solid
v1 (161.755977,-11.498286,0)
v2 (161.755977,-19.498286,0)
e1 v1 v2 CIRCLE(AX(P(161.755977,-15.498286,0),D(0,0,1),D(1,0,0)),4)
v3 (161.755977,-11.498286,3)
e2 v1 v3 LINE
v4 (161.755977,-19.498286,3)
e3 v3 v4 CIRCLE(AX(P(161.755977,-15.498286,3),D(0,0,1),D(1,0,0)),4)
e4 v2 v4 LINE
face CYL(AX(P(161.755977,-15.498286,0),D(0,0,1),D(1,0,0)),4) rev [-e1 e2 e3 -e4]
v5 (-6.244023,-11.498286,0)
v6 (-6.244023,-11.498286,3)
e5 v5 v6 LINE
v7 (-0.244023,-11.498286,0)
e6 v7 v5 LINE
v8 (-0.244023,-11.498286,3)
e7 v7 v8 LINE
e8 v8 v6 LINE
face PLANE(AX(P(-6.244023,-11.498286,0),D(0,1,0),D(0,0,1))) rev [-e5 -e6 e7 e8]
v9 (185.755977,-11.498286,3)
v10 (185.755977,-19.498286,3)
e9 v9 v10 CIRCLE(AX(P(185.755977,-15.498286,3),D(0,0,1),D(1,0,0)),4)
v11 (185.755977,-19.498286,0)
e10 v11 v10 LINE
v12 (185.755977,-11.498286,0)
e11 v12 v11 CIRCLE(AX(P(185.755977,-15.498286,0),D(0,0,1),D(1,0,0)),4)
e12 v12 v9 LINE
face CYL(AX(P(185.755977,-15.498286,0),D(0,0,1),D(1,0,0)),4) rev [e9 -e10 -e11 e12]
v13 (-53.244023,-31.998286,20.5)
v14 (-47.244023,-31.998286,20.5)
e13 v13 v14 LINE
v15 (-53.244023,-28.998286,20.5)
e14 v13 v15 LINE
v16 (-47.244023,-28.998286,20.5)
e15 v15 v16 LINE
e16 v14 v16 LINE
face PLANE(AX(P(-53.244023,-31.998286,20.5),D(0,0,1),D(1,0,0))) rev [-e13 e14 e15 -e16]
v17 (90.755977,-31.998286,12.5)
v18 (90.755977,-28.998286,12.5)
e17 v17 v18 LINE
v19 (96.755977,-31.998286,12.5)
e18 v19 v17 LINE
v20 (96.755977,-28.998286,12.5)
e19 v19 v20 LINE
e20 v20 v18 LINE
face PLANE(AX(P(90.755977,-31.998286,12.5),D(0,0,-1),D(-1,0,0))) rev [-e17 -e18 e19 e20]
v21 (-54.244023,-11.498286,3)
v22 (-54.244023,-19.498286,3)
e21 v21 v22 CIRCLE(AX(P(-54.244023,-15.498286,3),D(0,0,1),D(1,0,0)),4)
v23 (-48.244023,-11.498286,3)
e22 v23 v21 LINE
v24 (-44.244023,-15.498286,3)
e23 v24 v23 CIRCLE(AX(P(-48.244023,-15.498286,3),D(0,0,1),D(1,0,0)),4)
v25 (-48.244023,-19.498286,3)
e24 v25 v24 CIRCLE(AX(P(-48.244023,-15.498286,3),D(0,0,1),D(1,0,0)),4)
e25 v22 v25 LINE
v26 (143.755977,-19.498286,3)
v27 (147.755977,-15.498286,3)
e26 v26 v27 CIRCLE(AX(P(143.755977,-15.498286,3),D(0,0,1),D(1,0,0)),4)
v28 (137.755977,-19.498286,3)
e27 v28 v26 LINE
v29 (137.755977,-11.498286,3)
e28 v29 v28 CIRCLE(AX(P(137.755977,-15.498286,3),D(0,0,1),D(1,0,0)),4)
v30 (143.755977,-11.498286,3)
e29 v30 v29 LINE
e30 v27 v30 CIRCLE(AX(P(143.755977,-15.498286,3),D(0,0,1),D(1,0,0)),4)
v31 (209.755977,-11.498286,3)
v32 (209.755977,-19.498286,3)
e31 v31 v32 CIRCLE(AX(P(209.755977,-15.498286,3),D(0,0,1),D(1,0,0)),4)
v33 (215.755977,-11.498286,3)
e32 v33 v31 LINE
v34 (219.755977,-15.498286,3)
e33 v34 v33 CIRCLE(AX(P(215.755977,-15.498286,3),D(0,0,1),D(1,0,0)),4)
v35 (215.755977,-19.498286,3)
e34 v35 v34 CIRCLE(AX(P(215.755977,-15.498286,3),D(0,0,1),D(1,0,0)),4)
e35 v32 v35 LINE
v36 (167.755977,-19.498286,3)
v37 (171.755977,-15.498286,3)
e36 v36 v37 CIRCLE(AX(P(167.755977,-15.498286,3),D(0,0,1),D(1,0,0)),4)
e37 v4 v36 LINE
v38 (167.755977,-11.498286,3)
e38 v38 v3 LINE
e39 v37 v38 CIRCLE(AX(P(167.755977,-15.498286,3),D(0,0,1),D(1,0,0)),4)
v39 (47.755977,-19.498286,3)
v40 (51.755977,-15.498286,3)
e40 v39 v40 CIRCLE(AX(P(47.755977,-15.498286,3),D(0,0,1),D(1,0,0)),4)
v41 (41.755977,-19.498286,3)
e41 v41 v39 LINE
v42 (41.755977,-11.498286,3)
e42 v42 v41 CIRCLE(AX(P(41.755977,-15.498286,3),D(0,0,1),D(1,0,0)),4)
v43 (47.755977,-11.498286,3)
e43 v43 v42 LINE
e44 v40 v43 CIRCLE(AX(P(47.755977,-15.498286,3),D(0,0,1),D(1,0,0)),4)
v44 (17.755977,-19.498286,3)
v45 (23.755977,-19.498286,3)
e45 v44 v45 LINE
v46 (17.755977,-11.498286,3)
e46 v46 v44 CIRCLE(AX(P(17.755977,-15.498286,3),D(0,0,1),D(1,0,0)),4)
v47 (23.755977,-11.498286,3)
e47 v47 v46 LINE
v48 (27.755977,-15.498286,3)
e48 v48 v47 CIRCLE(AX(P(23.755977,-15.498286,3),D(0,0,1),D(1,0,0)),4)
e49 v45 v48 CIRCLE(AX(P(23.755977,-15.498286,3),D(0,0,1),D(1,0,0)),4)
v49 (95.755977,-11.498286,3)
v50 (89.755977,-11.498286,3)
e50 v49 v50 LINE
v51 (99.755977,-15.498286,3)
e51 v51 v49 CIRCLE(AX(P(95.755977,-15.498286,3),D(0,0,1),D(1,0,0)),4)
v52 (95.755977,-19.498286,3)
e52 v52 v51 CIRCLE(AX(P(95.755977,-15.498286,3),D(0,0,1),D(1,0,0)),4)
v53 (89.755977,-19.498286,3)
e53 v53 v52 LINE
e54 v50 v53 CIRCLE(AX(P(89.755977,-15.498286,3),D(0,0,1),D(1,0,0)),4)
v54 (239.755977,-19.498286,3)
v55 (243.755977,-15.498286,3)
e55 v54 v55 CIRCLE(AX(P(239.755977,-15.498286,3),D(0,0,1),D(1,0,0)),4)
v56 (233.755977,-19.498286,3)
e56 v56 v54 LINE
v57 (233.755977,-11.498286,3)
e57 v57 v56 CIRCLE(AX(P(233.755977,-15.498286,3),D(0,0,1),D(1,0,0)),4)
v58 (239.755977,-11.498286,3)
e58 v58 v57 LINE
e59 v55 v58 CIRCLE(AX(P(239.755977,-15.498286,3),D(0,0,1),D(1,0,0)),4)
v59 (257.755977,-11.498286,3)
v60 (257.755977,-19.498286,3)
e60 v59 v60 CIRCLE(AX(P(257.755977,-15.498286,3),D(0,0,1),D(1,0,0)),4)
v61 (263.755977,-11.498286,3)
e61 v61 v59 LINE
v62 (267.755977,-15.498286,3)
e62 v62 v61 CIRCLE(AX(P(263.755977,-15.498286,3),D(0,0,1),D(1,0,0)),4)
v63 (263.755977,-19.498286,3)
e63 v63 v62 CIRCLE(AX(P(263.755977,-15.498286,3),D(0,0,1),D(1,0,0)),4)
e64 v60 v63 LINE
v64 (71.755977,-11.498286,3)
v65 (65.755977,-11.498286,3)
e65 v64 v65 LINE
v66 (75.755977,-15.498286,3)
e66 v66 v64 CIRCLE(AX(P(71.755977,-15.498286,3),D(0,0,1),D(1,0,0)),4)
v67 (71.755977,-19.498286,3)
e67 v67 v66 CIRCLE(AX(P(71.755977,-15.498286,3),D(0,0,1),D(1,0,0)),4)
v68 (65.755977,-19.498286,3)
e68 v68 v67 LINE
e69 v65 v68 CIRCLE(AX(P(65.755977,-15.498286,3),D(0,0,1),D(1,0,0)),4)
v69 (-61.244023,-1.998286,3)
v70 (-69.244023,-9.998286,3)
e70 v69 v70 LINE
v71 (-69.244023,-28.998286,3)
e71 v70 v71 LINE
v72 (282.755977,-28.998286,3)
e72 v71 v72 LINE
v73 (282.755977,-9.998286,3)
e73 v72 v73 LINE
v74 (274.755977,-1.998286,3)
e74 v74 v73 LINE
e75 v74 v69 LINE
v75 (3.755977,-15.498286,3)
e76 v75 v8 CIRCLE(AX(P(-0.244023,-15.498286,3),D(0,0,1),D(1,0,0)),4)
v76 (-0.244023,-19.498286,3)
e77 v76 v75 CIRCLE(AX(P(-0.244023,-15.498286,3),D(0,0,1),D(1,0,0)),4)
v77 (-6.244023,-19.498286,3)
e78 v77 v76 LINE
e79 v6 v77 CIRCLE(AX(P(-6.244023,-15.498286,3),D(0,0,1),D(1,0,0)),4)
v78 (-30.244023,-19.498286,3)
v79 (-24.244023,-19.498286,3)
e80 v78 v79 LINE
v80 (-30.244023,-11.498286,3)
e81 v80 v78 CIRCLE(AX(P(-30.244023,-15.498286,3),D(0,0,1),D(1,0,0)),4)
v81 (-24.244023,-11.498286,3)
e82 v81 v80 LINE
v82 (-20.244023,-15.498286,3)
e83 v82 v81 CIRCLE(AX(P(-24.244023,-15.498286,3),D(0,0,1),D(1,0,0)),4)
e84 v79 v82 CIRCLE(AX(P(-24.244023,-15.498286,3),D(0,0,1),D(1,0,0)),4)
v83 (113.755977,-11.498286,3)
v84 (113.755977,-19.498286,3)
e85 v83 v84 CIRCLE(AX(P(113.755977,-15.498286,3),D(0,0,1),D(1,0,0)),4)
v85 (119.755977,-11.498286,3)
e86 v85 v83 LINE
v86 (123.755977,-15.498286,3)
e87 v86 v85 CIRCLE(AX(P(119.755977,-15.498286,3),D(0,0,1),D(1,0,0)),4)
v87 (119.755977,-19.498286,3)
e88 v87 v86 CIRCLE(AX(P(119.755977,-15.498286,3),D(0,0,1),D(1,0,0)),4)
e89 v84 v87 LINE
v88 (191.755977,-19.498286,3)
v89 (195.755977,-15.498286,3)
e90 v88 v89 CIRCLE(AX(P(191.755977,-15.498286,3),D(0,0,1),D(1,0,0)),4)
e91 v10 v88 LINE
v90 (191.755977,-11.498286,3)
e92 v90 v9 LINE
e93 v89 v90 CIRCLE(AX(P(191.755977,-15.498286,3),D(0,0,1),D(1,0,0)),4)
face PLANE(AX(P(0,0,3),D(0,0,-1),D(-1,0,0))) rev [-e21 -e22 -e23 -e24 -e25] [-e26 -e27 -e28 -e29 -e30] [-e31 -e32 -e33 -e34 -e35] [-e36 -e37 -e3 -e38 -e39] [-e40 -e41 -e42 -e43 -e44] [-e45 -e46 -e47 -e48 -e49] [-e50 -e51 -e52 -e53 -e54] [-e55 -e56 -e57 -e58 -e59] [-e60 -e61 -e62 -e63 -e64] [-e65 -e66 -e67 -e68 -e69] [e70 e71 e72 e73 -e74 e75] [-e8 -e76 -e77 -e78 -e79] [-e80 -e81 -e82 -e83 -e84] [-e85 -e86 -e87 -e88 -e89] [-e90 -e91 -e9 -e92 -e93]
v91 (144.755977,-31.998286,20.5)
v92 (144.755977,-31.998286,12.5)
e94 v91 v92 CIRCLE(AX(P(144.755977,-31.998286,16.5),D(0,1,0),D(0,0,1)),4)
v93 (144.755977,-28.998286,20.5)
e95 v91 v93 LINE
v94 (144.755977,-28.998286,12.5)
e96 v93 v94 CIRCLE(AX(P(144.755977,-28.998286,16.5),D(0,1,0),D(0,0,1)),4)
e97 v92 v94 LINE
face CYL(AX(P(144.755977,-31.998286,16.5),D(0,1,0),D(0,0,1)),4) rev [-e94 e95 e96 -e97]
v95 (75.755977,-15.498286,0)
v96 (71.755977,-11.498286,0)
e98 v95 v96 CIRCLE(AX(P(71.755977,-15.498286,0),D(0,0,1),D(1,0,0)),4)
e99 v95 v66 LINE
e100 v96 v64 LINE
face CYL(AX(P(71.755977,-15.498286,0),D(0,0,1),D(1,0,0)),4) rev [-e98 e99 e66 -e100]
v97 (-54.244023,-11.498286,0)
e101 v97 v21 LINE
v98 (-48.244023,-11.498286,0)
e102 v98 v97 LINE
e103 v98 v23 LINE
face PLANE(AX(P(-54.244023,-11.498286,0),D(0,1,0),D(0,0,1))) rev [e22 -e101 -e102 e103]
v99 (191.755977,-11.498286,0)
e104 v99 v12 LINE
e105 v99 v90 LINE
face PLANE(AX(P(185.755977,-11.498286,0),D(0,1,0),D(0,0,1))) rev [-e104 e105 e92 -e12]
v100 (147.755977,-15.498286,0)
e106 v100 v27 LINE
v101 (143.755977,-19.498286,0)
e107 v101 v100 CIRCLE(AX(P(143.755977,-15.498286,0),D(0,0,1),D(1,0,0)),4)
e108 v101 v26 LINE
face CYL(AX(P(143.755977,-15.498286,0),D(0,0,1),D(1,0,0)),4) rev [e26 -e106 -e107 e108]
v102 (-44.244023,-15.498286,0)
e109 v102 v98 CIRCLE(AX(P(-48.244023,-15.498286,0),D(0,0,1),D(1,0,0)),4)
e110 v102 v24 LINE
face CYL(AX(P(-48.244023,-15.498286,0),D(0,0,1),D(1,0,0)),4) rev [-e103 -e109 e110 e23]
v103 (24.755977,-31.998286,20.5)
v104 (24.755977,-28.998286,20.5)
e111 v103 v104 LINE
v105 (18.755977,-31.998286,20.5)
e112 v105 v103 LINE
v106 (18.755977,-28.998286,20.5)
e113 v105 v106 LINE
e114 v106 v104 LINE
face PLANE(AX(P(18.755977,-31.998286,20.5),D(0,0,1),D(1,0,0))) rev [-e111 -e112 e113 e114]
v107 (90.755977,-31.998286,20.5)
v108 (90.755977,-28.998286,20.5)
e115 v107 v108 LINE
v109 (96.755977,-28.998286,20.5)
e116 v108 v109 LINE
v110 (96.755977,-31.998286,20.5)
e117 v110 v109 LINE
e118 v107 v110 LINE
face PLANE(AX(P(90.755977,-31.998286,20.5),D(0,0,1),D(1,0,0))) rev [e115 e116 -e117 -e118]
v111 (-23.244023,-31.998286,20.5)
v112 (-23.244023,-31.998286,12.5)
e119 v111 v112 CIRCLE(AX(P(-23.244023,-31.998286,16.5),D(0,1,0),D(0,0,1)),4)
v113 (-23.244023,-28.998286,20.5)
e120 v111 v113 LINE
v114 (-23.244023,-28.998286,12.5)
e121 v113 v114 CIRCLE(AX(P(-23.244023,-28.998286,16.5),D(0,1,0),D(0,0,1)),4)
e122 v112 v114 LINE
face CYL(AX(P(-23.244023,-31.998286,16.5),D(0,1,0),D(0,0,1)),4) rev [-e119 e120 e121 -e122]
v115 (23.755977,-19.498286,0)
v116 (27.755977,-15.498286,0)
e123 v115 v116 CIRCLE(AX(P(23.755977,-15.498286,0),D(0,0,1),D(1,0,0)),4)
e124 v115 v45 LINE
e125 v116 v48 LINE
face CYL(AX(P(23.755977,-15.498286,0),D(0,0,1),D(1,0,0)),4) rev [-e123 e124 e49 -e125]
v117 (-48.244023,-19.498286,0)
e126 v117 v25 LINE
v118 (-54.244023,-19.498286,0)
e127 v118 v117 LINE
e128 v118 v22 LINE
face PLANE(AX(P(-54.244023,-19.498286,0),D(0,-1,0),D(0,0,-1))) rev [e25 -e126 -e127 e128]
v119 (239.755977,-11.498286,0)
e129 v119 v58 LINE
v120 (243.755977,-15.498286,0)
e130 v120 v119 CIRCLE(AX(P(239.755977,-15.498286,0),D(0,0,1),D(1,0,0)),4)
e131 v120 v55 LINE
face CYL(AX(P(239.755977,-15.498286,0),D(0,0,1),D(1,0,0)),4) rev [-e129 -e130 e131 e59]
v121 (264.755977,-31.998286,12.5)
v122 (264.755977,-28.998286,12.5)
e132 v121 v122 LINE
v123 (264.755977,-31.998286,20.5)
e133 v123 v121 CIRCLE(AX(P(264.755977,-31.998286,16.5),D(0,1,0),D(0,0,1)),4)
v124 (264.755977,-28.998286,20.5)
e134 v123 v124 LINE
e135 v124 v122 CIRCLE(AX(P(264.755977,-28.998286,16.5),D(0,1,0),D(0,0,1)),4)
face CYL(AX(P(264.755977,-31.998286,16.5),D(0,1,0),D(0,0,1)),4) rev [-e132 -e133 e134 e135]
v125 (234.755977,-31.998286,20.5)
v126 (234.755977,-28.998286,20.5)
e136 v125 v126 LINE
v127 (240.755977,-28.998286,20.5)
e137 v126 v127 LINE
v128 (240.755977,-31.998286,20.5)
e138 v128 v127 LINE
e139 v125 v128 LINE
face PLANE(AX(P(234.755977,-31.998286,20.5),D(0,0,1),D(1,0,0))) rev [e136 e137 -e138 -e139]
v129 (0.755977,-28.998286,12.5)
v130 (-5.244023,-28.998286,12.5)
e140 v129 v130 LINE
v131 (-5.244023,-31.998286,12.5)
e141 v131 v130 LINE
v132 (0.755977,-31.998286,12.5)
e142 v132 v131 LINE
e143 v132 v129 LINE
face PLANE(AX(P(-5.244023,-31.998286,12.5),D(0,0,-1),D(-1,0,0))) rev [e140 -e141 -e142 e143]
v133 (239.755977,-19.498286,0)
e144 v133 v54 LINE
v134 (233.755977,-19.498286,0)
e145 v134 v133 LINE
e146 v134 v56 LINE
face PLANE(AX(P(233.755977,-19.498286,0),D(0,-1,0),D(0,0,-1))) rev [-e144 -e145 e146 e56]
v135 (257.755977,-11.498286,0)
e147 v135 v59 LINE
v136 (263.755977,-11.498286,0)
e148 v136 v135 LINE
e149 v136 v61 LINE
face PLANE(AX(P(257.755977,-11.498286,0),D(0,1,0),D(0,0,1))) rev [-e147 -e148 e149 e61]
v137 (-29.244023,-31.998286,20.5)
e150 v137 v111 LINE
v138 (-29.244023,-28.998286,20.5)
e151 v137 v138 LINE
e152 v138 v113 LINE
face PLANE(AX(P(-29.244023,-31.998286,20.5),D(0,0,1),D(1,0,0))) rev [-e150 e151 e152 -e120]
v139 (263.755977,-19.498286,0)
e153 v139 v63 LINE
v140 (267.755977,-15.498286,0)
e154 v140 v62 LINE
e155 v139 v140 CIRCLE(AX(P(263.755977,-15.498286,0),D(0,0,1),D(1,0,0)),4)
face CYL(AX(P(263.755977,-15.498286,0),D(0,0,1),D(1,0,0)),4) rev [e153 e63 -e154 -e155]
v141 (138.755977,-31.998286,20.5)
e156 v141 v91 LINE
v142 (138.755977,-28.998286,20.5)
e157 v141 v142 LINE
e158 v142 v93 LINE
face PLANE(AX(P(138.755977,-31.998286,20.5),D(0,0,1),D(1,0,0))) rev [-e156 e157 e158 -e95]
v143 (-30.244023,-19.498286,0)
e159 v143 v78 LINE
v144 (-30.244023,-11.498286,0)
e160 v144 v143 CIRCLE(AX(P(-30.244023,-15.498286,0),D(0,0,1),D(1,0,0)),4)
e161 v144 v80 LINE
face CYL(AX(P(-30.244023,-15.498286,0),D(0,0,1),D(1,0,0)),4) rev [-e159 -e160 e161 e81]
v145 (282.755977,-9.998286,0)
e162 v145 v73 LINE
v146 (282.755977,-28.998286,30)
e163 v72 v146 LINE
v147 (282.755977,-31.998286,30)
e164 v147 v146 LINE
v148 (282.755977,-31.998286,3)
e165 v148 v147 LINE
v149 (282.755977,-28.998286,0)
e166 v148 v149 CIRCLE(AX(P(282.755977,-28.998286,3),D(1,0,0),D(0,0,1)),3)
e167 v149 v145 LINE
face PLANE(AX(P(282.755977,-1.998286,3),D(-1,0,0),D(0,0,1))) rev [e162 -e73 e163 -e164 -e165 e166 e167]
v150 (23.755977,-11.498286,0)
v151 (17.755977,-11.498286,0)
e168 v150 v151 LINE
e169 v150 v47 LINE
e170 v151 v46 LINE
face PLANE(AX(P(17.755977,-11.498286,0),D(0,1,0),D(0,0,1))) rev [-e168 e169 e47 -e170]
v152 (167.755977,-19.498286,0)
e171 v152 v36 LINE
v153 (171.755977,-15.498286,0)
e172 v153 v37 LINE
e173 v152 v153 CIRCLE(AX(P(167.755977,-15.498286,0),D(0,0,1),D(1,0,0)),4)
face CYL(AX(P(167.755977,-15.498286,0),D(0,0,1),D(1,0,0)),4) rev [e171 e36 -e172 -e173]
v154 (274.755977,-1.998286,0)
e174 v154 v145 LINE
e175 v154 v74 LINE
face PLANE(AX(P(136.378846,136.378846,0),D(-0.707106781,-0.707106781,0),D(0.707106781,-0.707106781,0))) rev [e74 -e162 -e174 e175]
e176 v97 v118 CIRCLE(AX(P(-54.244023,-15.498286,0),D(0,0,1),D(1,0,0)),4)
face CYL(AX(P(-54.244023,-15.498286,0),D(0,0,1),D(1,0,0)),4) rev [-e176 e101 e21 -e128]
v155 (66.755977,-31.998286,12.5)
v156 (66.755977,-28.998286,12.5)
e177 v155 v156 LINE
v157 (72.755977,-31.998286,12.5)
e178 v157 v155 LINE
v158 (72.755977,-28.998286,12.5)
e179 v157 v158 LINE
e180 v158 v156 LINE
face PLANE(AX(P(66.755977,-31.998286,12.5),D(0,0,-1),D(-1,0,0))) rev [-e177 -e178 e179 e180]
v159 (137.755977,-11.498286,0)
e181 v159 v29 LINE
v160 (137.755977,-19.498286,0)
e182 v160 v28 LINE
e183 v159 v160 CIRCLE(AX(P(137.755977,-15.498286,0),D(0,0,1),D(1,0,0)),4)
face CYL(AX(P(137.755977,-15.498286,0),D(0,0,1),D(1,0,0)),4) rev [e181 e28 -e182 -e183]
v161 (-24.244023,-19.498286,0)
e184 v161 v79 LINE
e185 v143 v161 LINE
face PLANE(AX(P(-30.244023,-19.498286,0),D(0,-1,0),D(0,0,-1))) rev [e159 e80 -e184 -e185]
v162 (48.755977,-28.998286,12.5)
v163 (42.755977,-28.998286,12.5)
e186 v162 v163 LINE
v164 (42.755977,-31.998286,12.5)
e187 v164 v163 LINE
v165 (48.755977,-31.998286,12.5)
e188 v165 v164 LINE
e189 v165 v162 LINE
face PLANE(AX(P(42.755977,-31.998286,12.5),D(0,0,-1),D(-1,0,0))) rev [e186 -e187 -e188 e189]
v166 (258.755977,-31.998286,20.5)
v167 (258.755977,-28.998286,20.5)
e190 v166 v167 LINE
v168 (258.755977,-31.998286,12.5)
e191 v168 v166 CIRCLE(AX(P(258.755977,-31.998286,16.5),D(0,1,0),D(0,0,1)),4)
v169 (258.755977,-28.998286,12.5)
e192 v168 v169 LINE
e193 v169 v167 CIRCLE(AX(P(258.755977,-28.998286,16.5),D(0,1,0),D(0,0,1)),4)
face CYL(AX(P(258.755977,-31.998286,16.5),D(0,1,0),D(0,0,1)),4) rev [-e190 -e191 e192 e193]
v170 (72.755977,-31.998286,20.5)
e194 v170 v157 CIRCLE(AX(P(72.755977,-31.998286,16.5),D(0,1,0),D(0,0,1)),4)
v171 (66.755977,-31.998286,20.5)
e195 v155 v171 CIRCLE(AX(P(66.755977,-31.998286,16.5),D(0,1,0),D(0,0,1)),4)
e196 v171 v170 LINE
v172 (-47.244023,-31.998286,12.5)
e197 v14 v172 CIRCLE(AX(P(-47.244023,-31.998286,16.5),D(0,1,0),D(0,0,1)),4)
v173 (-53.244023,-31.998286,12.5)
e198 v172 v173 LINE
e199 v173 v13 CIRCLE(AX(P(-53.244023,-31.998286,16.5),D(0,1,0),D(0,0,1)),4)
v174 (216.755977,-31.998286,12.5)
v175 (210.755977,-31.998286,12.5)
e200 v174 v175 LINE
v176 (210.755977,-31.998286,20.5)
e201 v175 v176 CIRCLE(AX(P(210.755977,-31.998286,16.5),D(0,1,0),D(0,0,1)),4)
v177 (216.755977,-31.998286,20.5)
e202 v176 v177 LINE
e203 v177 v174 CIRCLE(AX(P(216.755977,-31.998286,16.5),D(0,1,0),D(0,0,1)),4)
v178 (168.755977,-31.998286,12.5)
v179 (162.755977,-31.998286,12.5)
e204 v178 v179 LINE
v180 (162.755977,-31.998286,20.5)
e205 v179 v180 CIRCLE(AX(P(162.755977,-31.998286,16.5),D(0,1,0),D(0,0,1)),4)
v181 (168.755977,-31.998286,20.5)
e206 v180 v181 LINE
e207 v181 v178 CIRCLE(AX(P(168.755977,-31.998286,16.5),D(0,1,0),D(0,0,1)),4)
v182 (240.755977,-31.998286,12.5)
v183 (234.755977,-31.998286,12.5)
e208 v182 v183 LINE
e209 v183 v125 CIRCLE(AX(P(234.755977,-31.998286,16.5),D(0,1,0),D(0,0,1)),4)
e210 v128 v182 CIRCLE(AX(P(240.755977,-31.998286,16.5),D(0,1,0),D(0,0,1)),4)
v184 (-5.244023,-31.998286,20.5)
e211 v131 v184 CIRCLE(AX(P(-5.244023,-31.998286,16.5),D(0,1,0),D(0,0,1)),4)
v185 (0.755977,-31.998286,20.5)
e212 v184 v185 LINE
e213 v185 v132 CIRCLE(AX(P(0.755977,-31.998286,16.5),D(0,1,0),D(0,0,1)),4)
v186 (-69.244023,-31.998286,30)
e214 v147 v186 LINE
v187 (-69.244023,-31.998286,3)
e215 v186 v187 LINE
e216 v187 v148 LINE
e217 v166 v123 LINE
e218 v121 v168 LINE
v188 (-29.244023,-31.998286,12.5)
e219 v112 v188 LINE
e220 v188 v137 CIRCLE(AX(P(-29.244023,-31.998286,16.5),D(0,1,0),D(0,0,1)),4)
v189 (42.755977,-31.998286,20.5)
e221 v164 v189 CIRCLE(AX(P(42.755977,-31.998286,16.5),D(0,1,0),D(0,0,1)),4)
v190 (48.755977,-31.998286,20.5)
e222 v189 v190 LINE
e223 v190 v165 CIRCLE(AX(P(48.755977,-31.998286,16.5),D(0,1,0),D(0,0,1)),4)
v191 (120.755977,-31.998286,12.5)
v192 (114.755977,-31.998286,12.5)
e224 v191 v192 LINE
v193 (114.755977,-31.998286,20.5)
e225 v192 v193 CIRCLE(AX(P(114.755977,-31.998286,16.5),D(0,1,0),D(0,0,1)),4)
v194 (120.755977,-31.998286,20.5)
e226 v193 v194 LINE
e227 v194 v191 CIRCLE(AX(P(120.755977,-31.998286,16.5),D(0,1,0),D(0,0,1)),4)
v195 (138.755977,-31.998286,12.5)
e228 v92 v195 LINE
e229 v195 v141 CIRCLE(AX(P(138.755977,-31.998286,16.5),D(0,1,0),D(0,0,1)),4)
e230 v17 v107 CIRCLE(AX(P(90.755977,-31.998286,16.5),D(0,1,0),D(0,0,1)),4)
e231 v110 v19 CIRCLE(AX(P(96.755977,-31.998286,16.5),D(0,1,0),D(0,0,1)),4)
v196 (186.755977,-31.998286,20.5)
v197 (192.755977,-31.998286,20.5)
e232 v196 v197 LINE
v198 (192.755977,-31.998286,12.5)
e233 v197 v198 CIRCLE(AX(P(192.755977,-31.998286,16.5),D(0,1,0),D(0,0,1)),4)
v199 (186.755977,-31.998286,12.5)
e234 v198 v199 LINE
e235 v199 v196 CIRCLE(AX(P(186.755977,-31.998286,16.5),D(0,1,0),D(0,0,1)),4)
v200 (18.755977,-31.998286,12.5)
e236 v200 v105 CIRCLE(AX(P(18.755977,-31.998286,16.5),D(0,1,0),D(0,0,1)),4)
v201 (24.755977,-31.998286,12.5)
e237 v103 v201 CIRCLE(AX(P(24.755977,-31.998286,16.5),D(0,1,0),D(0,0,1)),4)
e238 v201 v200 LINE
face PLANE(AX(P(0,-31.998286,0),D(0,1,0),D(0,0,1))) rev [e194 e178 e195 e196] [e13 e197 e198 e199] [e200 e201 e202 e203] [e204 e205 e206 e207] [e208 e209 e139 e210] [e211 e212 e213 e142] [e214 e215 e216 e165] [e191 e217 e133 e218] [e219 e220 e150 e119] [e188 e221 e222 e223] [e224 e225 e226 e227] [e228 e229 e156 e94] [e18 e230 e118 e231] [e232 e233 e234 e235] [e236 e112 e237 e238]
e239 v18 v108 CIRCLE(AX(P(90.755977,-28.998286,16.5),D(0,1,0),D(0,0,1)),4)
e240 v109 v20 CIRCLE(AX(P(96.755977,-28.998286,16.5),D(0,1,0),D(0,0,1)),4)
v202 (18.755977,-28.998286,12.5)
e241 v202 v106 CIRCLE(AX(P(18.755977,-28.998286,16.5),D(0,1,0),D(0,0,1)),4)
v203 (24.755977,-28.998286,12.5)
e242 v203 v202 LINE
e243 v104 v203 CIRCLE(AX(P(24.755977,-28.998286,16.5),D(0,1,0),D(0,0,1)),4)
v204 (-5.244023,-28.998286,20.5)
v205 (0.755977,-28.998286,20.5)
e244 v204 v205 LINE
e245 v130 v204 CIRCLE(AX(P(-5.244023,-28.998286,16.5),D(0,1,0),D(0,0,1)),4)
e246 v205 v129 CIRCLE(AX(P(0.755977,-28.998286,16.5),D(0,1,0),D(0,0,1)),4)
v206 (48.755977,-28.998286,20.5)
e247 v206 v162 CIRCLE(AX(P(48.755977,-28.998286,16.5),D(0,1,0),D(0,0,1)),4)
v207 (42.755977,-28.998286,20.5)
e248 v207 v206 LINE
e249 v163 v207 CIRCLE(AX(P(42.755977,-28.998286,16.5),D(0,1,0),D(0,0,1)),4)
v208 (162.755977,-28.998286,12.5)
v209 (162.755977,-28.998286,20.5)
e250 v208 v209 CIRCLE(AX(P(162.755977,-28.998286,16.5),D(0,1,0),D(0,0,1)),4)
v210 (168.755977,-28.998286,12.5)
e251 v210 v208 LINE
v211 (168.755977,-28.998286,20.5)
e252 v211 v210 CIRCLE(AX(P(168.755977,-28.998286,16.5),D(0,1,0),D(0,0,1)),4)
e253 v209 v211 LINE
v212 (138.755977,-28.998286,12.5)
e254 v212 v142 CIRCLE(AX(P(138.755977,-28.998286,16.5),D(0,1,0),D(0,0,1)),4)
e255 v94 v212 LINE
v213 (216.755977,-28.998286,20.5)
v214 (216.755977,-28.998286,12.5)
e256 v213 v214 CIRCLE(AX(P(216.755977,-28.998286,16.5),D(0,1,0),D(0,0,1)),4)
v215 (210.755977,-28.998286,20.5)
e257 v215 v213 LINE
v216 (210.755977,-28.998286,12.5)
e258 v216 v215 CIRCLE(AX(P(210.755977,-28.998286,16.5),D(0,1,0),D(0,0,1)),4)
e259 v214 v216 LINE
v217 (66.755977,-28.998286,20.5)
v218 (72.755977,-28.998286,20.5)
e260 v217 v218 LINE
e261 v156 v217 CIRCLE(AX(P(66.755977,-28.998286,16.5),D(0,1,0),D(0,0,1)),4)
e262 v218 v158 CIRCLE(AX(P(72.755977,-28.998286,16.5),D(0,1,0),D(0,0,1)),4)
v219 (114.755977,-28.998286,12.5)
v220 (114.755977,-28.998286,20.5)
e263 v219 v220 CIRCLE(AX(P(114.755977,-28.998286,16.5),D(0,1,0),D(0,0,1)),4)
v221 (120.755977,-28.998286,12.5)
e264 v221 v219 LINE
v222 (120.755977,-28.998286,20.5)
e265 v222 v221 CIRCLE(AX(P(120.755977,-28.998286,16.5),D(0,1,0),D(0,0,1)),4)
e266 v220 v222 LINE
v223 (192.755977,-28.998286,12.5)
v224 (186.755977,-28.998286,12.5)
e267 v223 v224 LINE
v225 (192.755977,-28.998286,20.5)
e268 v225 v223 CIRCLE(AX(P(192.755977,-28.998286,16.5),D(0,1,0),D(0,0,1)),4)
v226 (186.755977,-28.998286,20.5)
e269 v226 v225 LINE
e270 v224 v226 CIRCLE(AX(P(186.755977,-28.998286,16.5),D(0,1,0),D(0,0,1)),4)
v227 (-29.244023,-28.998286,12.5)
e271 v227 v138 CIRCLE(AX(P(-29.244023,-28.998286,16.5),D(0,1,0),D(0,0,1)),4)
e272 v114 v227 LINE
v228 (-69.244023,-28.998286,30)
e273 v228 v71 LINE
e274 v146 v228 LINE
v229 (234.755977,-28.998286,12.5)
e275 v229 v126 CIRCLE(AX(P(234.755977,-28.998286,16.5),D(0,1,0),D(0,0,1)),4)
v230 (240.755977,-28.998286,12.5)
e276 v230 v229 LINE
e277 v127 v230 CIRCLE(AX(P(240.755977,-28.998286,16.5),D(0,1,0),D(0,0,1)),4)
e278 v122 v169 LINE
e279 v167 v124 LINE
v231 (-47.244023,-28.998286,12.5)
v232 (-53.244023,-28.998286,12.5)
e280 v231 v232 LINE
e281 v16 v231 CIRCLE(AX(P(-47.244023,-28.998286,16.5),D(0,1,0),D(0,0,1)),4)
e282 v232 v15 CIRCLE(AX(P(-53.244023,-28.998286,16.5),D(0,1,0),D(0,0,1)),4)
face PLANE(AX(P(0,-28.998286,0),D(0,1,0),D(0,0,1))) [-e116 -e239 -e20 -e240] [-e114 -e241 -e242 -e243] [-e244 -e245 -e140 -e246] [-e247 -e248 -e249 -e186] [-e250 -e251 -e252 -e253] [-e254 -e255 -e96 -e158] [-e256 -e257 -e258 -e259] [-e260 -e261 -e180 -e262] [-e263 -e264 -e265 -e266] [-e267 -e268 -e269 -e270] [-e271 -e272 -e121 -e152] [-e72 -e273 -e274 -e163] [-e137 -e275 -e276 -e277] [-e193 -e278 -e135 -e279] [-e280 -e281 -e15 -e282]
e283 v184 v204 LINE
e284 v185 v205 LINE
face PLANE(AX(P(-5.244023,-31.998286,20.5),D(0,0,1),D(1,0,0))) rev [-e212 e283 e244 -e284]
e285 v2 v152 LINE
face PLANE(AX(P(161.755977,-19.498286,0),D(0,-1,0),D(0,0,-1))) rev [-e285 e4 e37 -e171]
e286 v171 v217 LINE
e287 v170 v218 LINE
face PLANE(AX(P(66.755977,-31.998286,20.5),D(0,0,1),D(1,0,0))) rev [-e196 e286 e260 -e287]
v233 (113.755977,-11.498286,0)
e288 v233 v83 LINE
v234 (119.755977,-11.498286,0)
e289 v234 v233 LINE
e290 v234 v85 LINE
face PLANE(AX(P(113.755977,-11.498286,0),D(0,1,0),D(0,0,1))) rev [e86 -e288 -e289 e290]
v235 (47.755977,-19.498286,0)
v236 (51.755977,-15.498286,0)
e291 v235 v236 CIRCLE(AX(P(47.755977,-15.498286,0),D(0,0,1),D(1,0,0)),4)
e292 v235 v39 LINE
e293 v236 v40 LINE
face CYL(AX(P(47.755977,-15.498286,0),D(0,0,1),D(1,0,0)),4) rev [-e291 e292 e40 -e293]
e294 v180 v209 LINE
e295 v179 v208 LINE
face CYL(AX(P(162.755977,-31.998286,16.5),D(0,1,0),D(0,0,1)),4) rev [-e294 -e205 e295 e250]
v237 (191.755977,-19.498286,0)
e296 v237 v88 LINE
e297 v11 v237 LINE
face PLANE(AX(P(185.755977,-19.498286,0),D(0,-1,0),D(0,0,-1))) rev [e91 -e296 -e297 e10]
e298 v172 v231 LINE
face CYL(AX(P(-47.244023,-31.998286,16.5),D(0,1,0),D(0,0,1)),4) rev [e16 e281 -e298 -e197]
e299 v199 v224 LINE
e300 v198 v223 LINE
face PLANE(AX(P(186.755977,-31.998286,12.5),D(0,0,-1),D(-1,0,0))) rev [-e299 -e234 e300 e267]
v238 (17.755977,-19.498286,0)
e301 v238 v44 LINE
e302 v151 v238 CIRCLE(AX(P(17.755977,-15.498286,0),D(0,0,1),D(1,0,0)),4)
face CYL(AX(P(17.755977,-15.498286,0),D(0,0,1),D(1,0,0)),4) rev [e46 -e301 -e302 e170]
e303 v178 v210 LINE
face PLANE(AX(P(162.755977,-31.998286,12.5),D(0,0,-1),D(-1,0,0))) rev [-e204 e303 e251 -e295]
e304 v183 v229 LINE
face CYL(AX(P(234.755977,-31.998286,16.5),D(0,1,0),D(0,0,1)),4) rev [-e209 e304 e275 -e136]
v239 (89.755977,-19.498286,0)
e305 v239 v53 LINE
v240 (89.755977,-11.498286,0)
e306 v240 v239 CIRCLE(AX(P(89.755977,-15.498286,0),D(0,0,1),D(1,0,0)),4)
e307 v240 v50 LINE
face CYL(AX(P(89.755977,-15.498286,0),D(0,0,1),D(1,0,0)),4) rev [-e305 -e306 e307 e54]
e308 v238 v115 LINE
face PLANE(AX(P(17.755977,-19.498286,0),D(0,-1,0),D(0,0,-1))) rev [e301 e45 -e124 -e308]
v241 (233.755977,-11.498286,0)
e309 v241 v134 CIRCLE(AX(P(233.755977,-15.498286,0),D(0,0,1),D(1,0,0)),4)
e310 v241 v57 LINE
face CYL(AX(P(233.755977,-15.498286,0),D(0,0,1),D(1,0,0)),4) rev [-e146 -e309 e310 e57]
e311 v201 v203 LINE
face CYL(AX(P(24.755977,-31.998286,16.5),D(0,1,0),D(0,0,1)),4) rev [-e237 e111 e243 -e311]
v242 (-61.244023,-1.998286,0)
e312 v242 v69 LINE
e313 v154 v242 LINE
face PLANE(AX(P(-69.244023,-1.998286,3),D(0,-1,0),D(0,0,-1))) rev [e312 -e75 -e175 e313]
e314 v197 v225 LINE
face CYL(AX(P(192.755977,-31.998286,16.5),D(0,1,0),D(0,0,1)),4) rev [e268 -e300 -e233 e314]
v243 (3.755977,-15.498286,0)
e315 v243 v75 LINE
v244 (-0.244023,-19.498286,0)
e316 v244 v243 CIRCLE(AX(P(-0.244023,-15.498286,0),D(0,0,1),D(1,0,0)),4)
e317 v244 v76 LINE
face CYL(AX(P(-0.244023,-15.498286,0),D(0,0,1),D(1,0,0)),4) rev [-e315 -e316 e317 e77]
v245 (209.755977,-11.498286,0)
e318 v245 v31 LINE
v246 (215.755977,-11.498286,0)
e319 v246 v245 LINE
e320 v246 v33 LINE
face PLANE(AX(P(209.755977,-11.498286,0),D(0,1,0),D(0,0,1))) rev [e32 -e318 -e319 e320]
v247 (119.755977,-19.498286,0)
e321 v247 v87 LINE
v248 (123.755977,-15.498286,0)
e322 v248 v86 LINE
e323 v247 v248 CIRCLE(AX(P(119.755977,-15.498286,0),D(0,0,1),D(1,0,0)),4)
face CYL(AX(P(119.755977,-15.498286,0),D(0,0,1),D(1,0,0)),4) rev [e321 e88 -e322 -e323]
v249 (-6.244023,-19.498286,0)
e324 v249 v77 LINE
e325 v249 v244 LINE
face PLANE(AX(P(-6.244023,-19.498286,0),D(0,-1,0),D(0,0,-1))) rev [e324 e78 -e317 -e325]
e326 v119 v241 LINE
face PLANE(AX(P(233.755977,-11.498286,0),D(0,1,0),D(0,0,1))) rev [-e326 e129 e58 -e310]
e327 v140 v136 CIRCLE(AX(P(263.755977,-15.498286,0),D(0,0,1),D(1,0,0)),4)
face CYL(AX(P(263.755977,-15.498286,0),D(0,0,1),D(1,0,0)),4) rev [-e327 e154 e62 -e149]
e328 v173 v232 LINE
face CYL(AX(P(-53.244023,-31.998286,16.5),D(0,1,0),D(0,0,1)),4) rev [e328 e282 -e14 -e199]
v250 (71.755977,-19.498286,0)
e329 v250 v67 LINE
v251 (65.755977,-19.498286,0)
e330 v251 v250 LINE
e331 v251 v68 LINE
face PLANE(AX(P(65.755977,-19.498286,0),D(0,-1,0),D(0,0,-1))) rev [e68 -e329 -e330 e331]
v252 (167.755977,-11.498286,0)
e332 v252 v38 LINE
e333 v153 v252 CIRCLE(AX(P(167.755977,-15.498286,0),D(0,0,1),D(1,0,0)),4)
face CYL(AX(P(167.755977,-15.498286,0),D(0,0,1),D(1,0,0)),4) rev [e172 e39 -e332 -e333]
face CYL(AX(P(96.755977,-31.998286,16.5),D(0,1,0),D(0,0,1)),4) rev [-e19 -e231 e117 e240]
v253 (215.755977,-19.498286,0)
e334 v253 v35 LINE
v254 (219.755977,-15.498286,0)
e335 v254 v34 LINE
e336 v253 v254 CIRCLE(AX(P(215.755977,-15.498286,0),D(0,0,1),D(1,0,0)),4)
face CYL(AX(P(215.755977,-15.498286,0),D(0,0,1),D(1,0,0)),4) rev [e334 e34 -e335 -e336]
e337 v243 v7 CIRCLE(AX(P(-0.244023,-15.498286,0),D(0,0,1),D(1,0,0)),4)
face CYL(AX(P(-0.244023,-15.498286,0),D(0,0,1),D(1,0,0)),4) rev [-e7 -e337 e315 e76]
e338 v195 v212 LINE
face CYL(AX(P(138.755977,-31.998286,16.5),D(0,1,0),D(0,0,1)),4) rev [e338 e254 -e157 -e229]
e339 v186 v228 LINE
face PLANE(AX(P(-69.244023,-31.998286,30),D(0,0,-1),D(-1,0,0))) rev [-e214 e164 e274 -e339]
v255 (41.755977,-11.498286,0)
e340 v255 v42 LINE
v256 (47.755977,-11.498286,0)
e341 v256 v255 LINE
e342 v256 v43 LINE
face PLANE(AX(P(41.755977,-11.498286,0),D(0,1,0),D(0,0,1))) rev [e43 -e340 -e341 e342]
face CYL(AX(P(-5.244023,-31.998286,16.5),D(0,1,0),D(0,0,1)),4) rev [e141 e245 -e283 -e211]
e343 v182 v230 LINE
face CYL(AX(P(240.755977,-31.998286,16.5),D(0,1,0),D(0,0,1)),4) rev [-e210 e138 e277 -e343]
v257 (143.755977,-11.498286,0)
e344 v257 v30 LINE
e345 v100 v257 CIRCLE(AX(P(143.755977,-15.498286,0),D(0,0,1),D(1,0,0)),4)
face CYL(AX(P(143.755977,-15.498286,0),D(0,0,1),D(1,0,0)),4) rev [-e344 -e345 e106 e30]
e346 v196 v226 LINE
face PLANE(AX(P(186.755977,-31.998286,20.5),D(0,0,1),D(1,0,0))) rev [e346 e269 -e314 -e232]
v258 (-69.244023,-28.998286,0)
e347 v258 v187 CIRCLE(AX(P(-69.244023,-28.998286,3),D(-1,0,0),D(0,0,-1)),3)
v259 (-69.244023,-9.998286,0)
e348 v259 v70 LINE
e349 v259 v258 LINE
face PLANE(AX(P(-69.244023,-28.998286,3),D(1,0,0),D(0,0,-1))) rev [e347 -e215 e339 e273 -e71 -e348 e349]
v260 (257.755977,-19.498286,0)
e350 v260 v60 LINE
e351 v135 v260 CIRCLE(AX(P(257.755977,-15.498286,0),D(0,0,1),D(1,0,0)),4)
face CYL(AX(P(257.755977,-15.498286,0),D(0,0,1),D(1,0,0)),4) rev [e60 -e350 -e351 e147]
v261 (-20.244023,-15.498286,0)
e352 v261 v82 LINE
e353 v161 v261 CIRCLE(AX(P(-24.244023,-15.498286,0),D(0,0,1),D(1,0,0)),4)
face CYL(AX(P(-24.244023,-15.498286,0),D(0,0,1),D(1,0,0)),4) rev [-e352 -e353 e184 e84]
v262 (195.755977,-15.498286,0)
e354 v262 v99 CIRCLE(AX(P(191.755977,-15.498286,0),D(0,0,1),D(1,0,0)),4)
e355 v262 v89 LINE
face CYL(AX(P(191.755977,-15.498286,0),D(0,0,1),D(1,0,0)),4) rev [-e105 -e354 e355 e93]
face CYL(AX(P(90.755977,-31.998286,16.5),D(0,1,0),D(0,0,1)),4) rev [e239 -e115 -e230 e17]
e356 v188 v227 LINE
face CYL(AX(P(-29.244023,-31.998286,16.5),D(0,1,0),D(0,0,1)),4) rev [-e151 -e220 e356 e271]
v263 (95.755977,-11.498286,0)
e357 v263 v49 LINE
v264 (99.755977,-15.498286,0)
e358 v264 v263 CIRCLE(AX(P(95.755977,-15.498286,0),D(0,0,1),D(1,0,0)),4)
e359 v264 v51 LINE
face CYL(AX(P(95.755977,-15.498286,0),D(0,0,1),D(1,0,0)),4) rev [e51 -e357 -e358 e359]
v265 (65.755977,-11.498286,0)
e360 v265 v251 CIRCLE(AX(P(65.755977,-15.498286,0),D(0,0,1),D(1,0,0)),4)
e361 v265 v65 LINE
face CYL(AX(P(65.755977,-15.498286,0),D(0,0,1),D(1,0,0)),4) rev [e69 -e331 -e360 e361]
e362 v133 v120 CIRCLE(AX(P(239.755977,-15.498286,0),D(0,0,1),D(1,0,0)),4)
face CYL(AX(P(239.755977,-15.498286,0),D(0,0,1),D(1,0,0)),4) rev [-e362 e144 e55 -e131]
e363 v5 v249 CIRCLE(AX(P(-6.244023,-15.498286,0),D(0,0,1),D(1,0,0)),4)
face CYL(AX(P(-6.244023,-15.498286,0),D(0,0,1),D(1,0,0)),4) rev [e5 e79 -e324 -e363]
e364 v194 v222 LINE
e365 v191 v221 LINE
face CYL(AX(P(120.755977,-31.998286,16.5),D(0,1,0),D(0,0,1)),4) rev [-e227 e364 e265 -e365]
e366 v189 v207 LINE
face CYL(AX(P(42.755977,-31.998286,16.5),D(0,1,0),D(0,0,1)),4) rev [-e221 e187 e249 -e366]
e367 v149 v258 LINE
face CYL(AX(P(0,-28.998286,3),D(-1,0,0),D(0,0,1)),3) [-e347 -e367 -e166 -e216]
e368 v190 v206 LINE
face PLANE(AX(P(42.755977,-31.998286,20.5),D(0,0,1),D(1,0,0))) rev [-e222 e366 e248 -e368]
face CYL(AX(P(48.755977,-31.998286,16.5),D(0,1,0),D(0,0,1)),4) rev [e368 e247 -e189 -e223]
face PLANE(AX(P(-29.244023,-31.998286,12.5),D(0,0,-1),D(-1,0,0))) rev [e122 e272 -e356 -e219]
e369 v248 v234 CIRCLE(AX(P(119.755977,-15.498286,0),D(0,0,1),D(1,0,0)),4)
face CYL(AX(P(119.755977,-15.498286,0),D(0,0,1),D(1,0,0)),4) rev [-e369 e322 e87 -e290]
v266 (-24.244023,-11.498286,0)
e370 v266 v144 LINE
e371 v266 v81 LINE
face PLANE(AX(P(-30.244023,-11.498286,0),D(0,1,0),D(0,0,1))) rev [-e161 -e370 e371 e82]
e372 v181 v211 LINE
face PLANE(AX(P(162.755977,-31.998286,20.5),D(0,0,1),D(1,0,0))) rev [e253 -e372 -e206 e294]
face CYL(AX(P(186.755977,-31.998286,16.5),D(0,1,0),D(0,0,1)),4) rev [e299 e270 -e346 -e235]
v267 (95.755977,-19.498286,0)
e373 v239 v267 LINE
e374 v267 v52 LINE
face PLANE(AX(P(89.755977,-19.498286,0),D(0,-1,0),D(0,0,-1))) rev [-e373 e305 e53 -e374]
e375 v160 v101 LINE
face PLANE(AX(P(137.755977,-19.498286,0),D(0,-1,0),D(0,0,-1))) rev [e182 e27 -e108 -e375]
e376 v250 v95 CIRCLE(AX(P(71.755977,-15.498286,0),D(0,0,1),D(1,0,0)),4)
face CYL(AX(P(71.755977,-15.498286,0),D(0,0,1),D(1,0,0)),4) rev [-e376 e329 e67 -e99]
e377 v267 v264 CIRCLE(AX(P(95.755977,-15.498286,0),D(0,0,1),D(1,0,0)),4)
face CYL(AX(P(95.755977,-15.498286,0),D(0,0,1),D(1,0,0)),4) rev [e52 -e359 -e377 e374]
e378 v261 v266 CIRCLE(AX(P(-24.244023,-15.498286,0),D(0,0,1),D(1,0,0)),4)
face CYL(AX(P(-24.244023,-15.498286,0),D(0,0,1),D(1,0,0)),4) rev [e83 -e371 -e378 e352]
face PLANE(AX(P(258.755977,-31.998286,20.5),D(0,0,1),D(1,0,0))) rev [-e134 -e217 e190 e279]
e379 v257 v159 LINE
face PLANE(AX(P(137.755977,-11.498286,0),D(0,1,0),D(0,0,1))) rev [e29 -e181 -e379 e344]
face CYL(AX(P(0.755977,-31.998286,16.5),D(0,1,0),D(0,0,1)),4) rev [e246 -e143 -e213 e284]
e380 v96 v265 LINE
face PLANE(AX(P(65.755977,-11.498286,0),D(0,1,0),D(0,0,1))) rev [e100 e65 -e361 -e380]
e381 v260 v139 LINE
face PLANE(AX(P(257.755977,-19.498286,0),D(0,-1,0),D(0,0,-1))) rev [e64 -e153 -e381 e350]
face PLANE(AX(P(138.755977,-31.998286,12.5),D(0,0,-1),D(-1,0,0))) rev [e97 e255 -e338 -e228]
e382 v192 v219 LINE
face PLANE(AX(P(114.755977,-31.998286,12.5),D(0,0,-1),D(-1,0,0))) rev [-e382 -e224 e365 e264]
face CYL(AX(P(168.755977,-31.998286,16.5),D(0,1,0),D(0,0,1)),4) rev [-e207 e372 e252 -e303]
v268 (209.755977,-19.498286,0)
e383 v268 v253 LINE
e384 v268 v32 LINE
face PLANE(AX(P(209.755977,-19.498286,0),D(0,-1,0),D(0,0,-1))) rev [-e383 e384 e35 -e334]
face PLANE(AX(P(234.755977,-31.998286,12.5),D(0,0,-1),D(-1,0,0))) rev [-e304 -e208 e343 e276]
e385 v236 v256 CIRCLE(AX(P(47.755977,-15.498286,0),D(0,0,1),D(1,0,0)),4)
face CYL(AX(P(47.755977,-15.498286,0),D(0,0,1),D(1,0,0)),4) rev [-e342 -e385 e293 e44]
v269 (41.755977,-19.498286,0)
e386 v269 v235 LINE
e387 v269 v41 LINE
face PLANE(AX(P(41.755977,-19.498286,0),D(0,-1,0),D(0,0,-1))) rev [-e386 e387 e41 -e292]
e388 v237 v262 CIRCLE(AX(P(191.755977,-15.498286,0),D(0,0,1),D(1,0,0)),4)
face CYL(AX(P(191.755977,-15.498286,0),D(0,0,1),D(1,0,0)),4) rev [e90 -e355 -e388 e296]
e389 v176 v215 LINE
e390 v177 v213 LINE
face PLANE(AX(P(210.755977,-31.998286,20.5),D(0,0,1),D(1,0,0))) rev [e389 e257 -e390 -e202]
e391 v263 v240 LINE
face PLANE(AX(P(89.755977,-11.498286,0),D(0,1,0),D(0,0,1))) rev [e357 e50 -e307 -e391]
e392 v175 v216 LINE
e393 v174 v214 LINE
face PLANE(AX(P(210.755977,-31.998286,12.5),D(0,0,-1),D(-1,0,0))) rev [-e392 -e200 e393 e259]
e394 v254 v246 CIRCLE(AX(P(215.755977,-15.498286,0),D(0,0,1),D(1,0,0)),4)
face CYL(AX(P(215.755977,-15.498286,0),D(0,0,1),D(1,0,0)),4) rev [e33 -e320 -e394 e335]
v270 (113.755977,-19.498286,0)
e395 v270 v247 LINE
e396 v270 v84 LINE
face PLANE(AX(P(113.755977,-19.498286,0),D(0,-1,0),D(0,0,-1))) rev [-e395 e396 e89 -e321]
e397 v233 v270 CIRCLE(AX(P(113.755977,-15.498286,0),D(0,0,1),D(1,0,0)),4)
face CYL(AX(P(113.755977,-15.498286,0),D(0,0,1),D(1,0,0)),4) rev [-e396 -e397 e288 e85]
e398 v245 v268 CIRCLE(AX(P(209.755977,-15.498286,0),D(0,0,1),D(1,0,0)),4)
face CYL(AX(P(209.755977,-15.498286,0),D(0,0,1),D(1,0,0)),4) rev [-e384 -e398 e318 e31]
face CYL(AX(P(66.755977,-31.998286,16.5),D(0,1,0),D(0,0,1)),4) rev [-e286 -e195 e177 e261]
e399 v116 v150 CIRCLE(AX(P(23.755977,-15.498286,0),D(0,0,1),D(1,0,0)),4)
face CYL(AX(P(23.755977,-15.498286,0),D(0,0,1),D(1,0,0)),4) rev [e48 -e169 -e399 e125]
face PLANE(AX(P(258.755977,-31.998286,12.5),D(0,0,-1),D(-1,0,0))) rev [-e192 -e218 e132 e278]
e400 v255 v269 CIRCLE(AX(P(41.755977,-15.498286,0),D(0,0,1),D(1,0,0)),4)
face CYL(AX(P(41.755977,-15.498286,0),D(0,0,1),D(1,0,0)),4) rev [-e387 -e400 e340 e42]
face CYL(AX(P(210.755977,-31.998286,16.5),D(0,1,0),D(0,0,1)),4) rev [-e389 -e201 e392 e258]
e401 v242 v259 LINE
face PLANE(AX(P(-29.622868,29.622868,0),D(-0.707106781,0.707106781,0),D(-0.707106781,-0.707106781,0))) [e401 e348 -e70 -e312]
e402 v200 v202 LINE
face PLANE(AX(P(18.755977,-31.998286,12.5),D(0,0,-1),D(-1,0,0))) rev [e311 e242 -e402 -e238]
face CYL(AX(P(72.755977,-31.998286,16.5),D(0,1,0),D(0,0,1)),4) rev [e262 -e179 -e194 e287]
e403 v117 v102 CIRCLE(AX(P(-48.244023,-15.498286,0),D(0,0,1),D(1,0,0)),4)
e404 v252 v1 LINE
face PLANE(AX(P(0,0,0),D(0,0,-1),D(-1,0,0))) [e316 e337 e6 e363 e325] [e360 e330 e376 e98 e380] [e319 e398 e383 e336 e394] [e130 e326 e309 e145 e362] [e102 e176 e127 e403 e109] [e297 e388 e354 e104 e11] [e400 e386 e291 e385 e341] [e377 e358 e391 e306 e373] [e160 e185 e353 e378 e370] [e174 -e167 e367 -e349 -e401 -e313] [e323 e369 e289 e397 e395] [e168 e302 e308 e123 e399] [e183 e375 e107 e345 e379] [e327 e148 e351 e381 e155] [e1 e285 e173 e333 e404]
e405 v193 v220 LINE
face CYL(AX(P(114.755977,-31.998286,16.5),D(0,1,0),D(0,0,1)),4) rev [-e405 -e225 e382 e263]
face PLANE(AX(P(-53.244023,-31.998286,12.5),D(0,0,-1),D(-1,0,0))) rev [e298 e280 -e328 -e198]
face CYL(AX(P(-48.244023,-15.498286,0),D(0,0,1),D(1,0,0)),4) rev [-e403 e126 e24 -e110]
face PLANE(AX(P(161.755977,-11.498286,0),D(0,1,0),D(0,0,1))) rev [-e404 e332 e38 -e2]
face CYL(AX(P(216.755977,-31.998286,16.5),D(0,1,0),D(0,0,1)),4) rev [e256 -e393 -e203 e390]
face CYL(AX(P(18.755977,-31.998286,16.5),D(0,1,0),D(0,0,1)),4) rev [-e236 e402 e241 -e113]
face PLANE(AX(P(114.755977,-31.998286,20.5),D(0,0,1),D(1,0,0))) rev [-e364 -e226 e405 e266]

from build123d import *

# Parameters (mm, degrees)
SKETCH1_W           = 352
SKETCH1_H           = 27
BOSS_EXTRUDE1_DEPTH = 3
SKETCH3_W           = 352
SKETCH3_H           = 30
BOSS_EXTRUDE2_DEPTH = 3
FILLET1_R           = 3
CUT_EXTRUDE1_DEPTH  = 3
CUT_EXTRUDE2_DEPTH  = 3
CUT_EXTRUDE4_DEPTH  = 3


with BuildPart() as part:
    # Sketch1 → Boss-Extrude1 (new body)
    with BuildSketch(Plane.XY):
        with Locations((106.75597726, -15.498286177)):
            Rectangle(SKETCH1_W, SKETCH1_H)
    extrude(amount=BOSS_EXTRUDE1_DEPTH)

    # Sketch3 → Boss-Extrude2 (add)
    with BuildSketch(Plane.XZ.offset(28.998286177)):
        with Locations((106.75597726, 15)):
            Rectangle(SKETCH3_W, SKETCH3_H)
    extrude(amount=BOSS_EXTRUDE2_DEPTH)

    # Fillet1
    fillet1_edges = [part.edges().sort_by_distance(p)[0] for p in [
        (106.75597726, -31.998286177, 0),
    ]]
    fillet(fillet1_edges, radius=FILLET1_R)

    # Sketch4 → Cut-Extrude1 (cut)
    with BuildSketch(Plane(origin=(0, -28.998286177, 0), x_dir=(1, 0, 0), z_dir=(0, 1, 0))):
        with BuildLine():
            Line((-53.24402274, -12.5), (-47.24402274, -12.5))
            ThreePointArc((-47.24402274, -12.5), (-43.24402274, -16.5), (-47.24402274, -20.5))
            Line((-47.24402274, -20.5), (-53.24402274, -20.5))
            ThreePointArc((-53.24402274, -20.5), (-57.24402274, -16.5), (-53.24402274, -12.5))
        make_face()
        with BuildLine():
            Line((-29.24402274, -12.5), (-23.24402274, -12.5))
            ThreePointArc((-23.24402274, -12.5), (-19.24402274, -16.5), (-23.24402274, -20.5))
            Line((-23.24402274, -20.5), (-29.24402274, -20.5))
            ThreePointArc((-29.24402274, -20.5), (-33.24402274, -16.5), (-29.24402274, -12.5))
        make_face()
        with BuildLine():
            Line((-5.24402274, -12.5), (0.75597726, -12.5))
            ThreePointArc((0.75597726, -12.5), (4.75597726, -16.5), (0.75597726, -20.5))
            Line((0.75597726, -20.5), (-5.24402274, -20.5))
            ThreePointArc((-5.24402274, -20.5), (-9.24402274, -16.5), (-5.24402274, -12.5))
        make_face()
        with BuildLine():
            Line((18.75597726, -12.5), (24.75597726, -12.5))
            ThreePointArc((24.75597726, -12.5), (28.75597726, -16.5), (24.75597726, -20.5))
            Line((24.75597726, -20.5), (18.75597726, -20.5))
            ThreePointArc((18.75597726, -20.5), (14.75597726, -16.5), (18.75597726, -12.5))
        make_face()
        with BuildLine():
            Line((42.75597726, -12.5), (48.75597726, -12.5))
            ThreePointArc((48.75597726, -12.5), (52.75597726, -16.5), (48.75597726, -20.5))
            Line((48.75597726, -20.5), (42.75597726, -20.5))
            ThreePointArc((42.75597726, -20.5), (38.75597726, -16.5), (42.75597726, -12.5))
        make_face()
        with BuildLine():
            Line((66.75597726, -12.5), (72.75597726, -12.5))
            ThreePointArc((72.75597726, -12.5), (76.75597726, -16.5), (72.75597726, -20.5))
            Line((72.75597726, -20.5), (66.75597726, -20.5))
            ThreePointArc((66.75597726, -20.5), (62.75597726, -16.5), (66.75597726, -12.5))
        make_face()
        with BuildLine():
            Line((90.75597726, -12.5), (96.75597726, -12.5))
            ThreePointArc((96.75597726, -12.5), (100.75597726, -16.5), (96.75597726, -20.5))
            Line((96.75597726, -20.5), (90.75597726, -20.5))
            ThreePointArc((90.75597726, -20.5), (86.75597726, -16.5), (90.75597726, -12.5))
        make_face()
        with BuildLine():
            Line((114.75597726, -12.5), (120.75597726, -12.5))
            ThreePointArc((120.75597726, -12.5), (124.75597726, -16.5), (120.75597726, -20.5))
            Line((120.75597726, -20.5), (114.75597726, -20.5))
            ThreePointArc((114.75597726, -20.5), (110.75597726, -16.5), (114.75597726, -12.5))
        make_face()
        with BuildLine():
            Line((138.75597726, -12.5), (144.75597726, -12.5))
            ThreePointArc((144.75597726, -12.5), (148.75597726, -16.5), (144.75597726, -20.5))
            Line((144.75597726, -20.5), (138.75597726, -20.5))
            ThreePointArc((138.75597726, -20.5), (134.75597726, -16.5), (138.75597726, -12.5))
        make_face()
        with BuildLine():
            Line((162.75597726, -12.5), (168.75597726, -12.5))
            ThreePointArc((168.75597726, -12.5), (172.75597726, -16.5), (168.75597726, -20.5))
            Line((168.75597726, -20.5), (162.75597726, -20.5))
            ThreePointArc((162.75597726, -20.5), (158.75597726, -16.5), (162.75597726, -12.5))
        make_face()
        with BuildLine():
            Line((186.75597726, -12.5), (192.75597726, -12.5))
            ThreePointArc((192.75597726, -12.5), (196.75597726, -16.5), (192.75597726, -20.5))
            Line((192.75597726, -20.5), (186.75597726, -20.5))
            ThreePointArc((186.75597726, -20.5), (182.75597726, -16.5), (186.75597726, -12.5))
        make_face()
        with BuildLine():
            Line((210.75597726, -12.5), (216.75597726, -12.5))
            ThreePointArc((216.75597726, -12.5), (220.75597726, -16.5), (216.75597726, -20.5))
            Line((216.75597726, -20.5), (210.75597726, -20.5))
            ThreePointArc((210.75597726, -20.5), (206.75597726, -16.5), (210.75597726, -12.5))
        make_face()
        with BuildLine():
            Line((234.75597726, -12.5), (240.75597726, -12.5))
            ThreePointArc((240.75597726, -12.5), (244.75597726, -16.5), (240.75597726, -20.5))
            Line((240.75597726, -20.5), (234.75597726, -20.5))
            ThreePointArc((234.75597726, -20.5), (230.75597726, -16.5), (234.75597726, -12.5))
        make_face()
        with BuildLine():
            Line((258.75597726, -12.5), (264.75597726, -12.5))
            ThreePointArc((264.75597726, -12.5), (268.75597726, -16.5), (264.75597726, -20.5))
            Line((264.75597726, -20.5), (258.75597726, -20.5))
            ThreePointArc((258.75597726, -20.5), (254.75597726, -16.5), (258.75597726, -12.5))
        make_face()
    extrude(amount=-CUT_EXTRUDE1_DEPTH, mode=Mode.SUBTRACT)

    # Sketch5 → Cut-Extrude2 (cut)
    with BuildSketch(Plane.XY.offset(3)):
        with BuildLine():
            Line((-54.24402274, -11.498286177), (-48.24402274, -11.498286177))
            ThreePointArc((-48.24402274, -11.498286177), (-44.24402274, -15.498286177), (-48.24402274, -19.498286177))
            Line((-48.24402274, -19.498286177), (-54.24402274, -19.498286177))
            ThreePointArc((-54.24402274, -19.498286177), (-58.24402274, -15.498286177), (-54.24402274, -11.498286177))
        make_face()
        with BuildLine():
            Line((-30.24402274, -11.498286177), (-24.24402274, -11.498286177))
            ThreePointArc((-24.24402274, -11.498286177), (-20.24402274, -15.498286177), (-24.24402274, -19.498286177))
            Line((-24.24402274, -19.498286177), (-30.24402274, -19.498286177))
            ThreePointArc((-30.24402274, -19.498286177), (-34.24402274, -15.498286177), (-30.24402274, -11.498286177))
        make_face()
        with BuildLine():
            Line((-6.24402274, -11.498286177), (-0.24402274, -11.498286177))
            ThreePointArc((-0.24402274, -11.498286177), (3.75597726, -15.498286177), (-0.24402274, -19.498286177))
            Line((-0.24402274, -19.498286177), (-6.24402274, -19.498286177))
            ThreePointArc((-6.24402274, -19.498286177), (-10.24402274, -15.498286177), (-6.24402274, -11.498286177))
        make_face()
        with BuildLine():
            Line((17.75597726, -11.498286177), (23.75597726, -11.498286177))
            ThreePointArc((23.75597726, -11.498286177), (27.75597726, -15.498286177), (23.75597726, -19.498286177))
            Line((23.75597726, -19.498286177), (17.75597726, -19.498286177))
            ThreePointArc((17.75597726, -19.498286177), (13.75597726, -15.498286177), (17.75597726, -11.498286177))
        make_face()
        with BuildLine():
            Line((41.75597726, -11.498286177), (47.75597726, -11.498286177))
            ThreePointArc((47.75597726, -11.498286177), (51.75597726, -15.498286177), (47.75597726, -19.498286177))
            Line((47.75597726, -19.498286177), (41.75597726, -19.498286177))
            ThreePointArc((41.75597726, -19.498286177), (37.75597726, -15.498286177), (41.75597726, -11.498286177))
        make_face()
        with BuildLine():
            Line((65.75597726, -11.498286177), (71.75597726, -11.498286177))
            ThreePointArc((71.75597726, -11.498286177), (75.75597726, -15.498286177), (71.75597726, -19.498286177))
            Line((71.75597726, -19.498286177), (65.75597726, -19.498286177))
            ThreePointArc((65.75597726, -19.498286177), (61.75597726, -15.498286177), (65.75597726, -11.498286177))
        make_face()
        with BuildLine():
            Line((89.75597726, -11.498286177), (95.75597726, -11.498286177))
            ThreePointArc((95.75597726, -11.498286177), (99.75597726, -15.498286177), (95.75597726, -19.498286177))
            Line((95.75597726, -19.498286177), (89.75597726, -19.498286177))
            ThreePointArc((89.75597726, -19.498286177), (85.75597726, -15.498286177), (89.75597726, -11.498286177))
        make_face()
        with BuildLine():
            Line((113.75597726, -11.498286177), (119.75597726, -11.498286177))
            ThreePointArc((119.75597726, -11.498286177), (123.75597726, -15.498286177), (119.75597726, -19.498286177))
            Line((119.75597726, -19.498286177), (113.75597726, -19.498286177))
            ThreePointArc((113.75597726, -19.498286177), (109.75597726, -15.498286177), (113.75597726, -11.498286177))
        make_face()
        with BuildLine():
            Line((137.75597726, -11.498286177), (143.75597726, -11.498286177))
            ThreePointArc((143.75597726, -11.498286177), (147.75597726, -15.498286177), (143.75597726, -19.498286177))
            Line((143.75597726, -19.498286177), (137.75597726, -19.498286177))
            ThreePointArc((137.75597726, -19.498286177), (133.75597726, -15.498286177), (137.75597726, -11.498286177))
        make_face()
        with BuildLine():
            Line((161.75597726, -11.498286177), (167.75597726, -11.498286177))
            ThreePointArc((167.75597726, -11.498286177), (171.75597726, -15.498286177), (167.75597726, -19.498286177))
            Line((167.75597726, -19.498286177), (161.75597726, -19.498286177))
            ThreePointArc((161.75597726, -19.498286177), (157.75597726, -15.498286177), (161.75597726, -11.498286177))
        make_face()
        with BuildLine():
            Line((185.75597726, -11.498286177), (191.75597726, -11.498286177))
            ThreePointArc((191.75597726, -11.498286177), (195.75597726, -15.498286177), (191.75597726, -19.498286177))
            Line((191.75597726, -19.498286177), (185.75597726, -19.498286177))
            ThreePointArc((185.75597726, -19.498286177), (181.75597726, -15.498286177), (185.75597726, -11.498286177))
        make_face()
        with BuildLine():
            Line((209.75597726, -11.498286177), (215.75597726, -11.498286177))
            ThreePointArc((215.75597726, -11.498286177), (219.75597726, -15.498286177), (215.75597726, -19.498286177))
            Line((215.75597726, -19.498286177), (209.75597726, -19.498286177))
            ThreePointArc((209.75597726, -19.498286177), (205.75597726, -15.498286177), (209.75597726, -11.498286177))
        make_face()
        with BuildLine():
            Line((233.75597726, -11.498286177), (239.75597726, -11.498286177))
            ThreePointArc((239.75597726, -11.498286177), (243.75597726, -15.498286177), (239.75597726, -19.498286177))
            Line((239.75597726, -19.498286177), (233.75597726, -19.498286177))
            ThreePointArc((233.75597726, -19.498286177), (229.75597726, -15.498286177), (233.75597726, -11.498286177))
        make_face()
        with BuildLine():
            Line((257.75597726, -11.498286177), (263.75597726, -11.498286177))
            ThreePointArc((263.75597726, -11.498286177), (267.75597726, -15.498286177), (263.75597726, -19.498286177))
            Line((263.75597726, -19.498286177), (257.75597726, -19.498286177))
            ThreePointArc((257.75597726, -19.498286177), (253.75597726, -15.498286177), (257.75597726, -11.498286177))
        make_face()
    extrude(amount=-CUT_EXTRUDE2_DEPTH, mode=Mode.SUBTRACT)

    # Sketch6 → Cut-Extrude4 (cut)
    with BuildSketch(Plane.XY.offset(3)):
        Polygon((-69.24402274, -1.998286177), (-69.24402274, -7.998286177), (-69.24402274, -9.998286177), (-61.24402274, -1.998286177), align=None)
        Polygon((274.75597726, -1.998286177), (282.75597726, -1.998286177), (282.75597726, -9.998286177), align=None)
    extrude(amount=-CUT_EXTRUDE4_DEPTH, mode=Mode.SUBTRACT)


solid = part.part
